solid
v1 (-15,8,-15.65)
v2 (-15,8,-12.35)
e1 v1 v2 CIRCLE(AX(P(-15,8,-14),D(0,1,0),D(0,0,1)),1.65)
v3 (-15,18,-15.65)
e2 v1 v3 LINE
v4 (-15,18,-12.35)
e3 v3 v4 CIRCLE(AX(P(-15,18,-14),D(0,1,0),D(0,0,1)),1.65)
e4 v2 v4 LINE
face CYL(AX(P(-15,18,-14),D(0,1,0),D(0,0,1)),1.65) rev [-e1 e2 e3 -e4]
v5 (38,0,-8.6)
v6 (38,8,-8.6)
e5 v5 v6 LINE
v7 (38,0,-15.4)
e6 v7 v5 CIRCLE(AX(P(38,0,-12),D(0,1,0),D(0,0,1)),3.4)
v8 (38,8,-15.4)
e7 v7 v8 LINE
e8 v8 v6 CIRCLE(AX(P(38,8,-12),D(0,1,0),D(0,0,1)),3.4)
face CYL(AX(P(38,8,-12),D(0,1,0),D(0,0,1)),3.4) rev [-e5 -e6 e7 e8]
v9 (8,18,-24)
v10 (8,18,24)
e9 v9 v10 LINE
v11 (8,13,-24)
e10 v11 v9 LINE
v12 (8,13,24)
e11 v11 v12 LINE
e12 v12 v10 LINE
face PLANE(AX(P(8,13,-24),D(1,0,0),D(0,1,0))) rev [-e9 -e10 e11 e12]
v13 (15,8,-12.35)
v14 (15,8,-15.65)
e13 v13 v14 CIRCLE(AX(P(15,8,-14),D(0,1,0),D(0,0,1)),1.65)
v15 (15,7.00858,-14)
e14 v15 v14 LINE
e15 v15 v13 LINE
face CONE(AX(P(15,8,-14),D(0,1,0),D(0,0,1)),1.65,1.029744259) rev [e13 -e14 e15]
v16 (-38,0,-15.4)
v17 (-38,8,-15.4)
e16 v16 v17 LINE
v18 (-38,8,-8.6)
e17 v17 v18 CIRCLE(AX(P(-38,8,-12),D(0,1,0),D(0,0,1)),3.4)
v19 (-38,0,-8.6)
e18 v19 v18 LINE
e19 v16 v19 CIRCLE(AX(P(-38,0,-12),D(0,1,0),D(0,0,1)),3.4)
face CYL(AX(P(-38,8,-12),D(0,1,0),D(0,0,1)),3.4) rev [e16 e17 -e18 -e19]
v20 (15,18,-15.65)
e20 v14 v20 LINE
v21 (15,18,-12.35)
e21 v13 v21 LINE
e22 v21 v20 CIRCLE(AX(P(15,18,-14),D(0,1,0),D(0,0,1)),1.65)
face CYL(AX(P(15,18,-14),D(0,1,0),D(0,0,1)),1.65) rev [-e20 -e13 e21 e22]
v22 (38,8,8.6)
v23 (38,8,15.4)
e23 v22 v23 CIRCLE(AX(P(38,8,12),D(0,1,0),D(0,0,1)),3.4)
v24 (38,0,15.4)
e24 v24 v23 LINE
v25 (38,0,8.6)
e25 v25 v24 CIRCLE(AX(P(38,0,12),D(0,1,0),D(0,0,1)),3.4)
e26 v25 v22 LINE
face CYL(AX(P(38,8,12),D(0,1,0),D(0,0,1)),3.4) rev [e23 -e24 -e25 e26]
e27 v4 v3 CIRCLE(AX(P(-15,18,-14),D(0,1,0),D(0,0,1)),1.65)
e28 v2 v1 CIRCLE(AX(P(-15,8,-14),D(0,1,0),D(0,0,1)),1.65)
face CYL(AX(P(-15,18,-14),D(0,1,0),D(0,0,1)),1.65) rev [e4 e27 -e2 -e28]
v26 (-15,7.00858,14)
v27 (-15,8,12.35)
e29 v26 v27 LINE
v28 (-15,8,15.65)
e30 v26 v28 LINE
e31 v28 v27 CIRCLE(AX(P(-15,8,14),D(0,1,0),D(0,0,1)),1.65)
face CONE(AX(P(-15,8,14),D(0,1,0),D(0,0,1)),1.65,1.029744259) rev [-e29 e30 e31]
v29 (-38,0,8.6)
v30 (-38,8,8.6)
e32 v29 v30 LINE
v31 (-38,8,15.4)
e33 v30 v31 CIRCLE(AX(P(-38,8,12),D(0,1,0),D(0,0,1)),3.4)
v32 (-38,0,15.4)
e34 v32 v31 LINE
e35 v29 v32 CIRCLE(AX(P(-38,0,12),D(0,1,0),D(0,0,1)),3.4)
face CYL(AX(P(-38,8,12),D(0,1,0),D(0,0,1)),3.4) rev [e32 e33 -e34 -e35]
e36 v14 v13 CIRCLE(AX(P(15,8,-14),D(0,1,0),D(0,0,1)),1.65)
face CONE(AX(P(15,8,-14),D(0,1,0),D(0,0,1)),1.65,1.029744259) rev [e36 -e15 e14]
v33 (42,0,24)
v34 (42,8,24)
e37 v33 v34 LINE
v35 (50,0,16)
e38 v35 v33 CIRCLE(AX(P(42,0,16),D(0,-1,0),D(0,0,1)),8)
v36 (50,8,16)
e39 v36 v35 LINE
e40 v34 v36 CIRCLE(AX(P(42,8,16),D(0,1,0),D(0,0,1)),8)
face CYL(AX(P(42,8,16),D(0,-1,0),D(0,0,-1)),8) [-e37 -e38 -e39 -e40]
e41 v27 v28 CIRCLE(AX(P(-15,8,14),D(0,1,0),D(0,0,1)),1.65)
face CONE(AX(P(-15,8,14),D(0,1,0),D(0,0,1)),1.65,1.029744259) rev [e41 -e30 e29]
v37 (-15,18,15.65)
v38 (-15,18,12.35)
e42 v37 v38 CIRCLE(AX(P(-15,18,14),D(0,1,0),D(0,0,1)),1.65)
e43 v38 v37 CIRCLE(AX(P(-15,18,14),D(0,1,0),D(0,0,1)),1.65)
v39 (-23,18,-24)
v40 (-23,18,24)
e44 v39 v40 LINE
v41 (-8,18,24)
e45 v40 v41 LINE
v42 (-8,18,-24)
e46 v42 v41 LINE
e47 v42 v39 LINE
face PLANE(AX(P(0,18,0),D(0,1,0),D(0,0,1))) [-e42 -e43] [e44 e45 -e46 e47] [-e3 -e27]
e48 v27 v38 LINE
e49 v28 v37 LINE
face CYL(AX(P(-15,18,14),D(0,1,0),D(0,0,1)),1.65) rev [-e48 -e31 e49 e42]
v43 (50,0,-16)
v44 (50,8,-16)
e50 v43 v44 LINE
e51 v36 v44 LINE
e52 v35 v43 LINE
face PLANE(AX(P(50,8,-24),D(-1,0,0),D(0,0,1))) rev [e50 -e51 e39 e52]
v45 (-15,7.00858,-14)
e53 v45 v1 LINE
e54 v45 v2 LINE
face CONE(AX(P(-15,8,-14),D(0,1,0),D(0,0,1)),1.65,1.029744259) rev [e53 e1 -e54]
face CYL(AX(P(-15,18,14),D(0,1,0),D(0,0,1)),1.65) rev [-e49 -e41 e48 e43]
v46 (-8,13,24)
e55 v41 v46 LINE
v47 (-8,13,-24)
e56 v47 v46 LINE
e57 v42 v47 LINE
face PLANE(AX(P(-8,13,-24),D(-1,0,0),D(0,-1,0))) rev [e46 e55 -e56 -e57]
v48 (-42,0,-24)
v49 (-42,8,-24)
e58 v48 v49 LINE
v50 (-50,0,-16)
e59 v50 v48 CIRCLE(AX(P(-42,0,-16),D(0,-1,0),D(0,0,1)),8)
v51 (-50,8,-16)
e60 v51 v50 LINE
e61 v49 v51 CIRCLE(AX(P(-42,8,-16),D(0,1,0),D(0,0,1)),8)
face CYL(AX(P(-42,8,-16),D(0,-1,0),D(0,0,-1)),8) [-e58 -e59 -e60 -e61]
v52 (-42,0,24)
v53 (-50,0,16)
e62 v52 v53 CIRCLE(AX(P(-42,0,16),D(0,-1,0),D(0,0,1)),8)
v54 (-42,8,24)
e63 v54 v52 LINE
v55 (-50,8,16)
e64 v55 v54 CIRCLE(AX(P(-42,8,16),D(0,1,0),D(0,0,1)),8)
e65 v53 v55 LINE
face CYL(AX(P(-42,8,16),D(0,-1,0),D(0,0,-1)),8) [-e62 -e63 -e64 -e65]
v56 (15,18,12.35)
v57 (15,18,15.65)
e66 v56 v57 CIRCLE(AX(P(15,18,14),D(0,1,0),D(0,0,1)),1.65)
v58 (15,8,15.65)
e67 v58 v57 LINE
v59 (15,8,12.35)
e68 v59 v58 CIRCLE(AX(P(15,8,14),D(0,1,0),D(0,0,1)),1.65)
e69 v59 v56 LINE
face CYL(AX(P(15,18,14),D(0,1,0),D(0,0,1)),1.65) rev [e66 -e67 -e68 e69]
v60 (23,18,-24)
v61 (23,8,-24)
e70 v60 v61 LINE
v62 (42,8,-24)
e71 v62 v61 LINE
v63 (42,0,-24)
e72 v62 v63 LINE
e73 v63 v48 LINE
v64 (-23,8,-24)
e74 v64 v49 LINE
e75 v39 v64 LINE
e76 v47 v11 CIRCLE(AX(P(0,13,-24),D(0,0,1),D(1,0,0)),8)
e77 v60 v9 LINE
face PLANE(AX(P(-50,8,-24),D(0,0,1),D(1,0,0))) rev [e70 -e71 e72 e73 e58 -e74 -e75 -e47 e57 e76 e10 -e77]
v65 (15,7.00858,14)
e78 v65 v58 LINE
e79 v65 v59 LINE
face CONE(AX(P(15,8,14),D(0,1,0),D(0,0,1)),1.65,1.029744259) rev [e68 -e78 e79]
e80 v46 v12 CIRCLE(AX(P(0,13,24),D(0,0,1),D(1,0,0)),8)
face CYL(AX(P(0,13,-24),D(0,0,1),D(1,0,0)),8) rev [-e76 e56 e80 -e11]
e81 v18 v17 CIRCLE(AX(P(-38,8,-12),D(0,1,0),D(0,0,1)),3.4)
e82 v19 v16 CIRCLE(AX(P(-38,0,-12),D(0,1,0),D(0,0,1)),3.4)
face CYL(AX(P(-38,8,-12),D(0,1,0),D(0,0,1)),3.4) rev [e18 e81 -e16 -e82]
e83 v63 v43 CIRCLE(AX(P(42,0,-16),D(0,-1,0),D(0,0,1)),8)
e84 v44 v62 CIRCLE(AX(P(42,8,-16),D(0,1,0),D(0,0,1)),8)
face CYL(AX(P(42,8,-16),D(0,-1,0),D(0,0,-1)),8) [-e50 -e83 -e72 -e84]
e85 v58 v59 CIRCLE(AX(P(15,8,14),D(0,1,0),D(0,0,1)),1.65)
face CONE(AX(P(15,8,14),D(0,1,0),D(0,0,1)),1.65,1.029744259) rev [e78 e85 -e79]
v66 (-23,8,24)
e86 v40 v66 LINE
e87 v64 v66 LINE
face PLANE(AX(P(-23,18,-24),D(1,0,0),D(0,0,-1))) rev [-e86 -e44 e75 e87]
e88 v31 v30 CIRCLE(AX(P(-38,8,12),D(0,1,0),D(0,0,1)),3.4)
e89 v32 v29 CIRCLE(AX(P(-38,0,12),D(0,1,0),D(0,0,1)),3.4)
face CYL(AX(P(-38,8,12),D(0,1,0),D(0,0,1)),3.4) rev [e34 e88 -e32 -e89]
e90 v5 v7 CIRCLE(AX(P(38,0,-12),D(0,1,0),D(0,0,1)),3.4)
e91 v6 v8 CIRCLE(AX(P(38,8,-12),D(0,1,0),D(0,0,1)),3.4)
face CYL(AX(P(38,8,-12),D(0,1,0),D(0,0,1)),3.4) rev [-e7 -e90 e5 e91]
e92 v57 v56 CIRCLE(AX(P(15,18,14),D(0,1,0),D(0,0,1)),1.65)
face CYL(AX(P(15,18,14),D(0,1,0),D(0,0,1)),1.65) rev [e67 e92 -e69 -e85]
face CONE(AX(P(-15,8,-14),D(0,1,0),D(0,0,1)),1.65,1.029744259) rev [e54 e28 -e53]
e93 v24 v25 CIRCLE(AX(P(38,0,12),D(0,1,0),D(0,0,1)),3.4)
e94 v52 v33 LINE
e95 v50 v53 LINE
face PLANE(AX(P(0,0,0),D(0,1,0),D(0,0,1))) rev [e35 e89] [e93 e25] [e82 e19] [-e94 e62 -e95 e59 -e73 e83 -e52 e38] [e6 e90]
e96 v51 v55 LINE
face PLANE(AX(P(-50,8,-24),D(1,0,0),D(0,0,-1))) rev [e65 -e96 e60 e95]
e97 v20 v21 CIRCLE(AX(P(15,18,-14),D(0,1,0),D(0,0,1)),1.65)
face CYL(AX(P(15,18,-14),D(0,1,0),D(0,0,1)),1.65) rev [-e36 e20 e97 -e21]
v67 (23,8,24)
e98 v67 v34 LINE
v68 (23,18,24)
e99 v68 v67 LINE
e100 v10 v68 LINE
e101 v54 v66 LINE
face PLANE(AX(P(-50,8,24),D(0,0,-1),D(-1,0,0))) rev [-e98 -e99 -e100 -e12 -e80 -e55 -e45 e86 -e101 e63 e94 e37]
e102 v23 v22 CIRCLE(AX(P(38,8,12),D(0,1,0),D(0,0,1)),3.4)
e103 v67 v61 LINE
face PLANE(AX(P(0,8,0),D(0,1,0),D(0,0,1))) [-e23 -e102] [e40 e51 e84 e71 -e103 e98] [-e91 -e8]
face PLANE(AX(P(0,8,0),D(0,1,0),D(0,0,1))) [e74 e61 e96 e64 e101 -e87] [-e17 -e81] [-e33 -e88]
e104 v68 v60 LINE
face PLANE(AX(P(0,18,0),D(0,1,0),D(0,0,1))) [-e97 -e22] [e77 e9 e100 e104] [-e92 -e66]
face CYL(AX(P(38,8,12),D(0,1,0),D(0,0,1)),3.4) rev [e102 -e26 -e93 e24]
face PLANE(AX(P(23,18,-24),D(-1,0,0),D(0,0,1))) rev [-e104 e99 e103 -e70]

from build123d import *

# Parameters (mm, degrees)
SKETCH1_W             = 100
SKETCH1_H             = 48
BOSS_EXTRUDE1_DEPTH   = 8
SKETCH2_W             = 46
SKETCH2_H             = 48
BOSS_EXTRUDE2_DEPTH   = 10
CUT_EXTRUDE1_DEPTH    = 72.61005516
FILLET1_R             = 8
M4_TAPPED_HOLE1_D     = 3.3
M4_TAPPED_HOLE1_DEPTH = 10
M4_TAPPED_HOLE1_TIP   = 0.991420021
M8_TAPPED_HOLE1_D     = 6.8


with BuildPart() as part:
    # Sketch1 → Boss-Extrude1 (new body)
    with BuildSketch(Plane(origin=(0, 0, 0), x_dir=(1, 0, 0), z_dir=(0, 1, 0))):
        Rectangle(SKETCH1_W, SKETCH1_H)
    extrude(amount=BOSS_EXTRUDE1_DEPTH)

    # Sketch2 → Boss-Extrude2 (add)
    with BuildSketch(Plane(origin=(0, 8, 0), x_dir=(1, 0, 0), z_dir=(0, 1, 0))):
        Rectangle(SKETCH2_W, SKETCH2_H)
    extrude(amount=BOSS_EXTRUDE2_DEPTH)

    # Sketch3 → Cut-Extrude1 (cut, through all)
    with BuildSketch(Plane.XY.offset(24)):
        with BuildLine():
            Line((-8, 13), (-8, 18))
            Line((-8, 18), (8, 18))
            Line((8, 18), (8, 13))
            ThreePointArc((8, 13), (0, 5), (-8, 13))
        make_face()
    extrude(amount=-CUT_EXTRUDE1_DEPTH, mode=Mode.SUBTRACT)

    # Fillet1
    fillet1_edges = [part.edges().sort_by_distance(p)[0] for p in [
        (50, 4, 24),
        (-50, 4, 24),
        (-50, 4, -24),
        (50, 4, -24),
    ]]
    fillet(fillet1_edges, radius=FILLET1_R)

    # M4 Tapped Hole1
    with Locations(Plane(origin=(0, 18, 0), x_dir=(1, 0, 0), z_dir=(0, 1, 0))):
        with Locations((-15, 14), (-15, -14), (15, -14), (15, 14)):
            Hole(M4_TAPPED_HOLE1_D / 2, depth=M4_TAPPED_HOLE1_DEPTH)
            with Locations((0, 0, -(M4_TAPPED_HOLE1_DEPTH + M4_TAPPED_HOLE1_TIP / 2))):  # 118° drill point
                Cone(0, M4_TAPPED_HOLE1_D / 2, M4_TAPPED_HOLE1_TIP, mode=Mode.SUBTRACT)

    # M8 Tapped Hole1 (through all)
    with Locations(Plane(origin=(0, 8, 0), x_dir=(1, 0, 0), z_dir=(0, 1, 0))):
        with Locations((-38, 12), (-38, -12), (38, -12), (38, 12)):
            Hole(M8_TAPPED_HOLE1_D / 2)


solid = part.part
